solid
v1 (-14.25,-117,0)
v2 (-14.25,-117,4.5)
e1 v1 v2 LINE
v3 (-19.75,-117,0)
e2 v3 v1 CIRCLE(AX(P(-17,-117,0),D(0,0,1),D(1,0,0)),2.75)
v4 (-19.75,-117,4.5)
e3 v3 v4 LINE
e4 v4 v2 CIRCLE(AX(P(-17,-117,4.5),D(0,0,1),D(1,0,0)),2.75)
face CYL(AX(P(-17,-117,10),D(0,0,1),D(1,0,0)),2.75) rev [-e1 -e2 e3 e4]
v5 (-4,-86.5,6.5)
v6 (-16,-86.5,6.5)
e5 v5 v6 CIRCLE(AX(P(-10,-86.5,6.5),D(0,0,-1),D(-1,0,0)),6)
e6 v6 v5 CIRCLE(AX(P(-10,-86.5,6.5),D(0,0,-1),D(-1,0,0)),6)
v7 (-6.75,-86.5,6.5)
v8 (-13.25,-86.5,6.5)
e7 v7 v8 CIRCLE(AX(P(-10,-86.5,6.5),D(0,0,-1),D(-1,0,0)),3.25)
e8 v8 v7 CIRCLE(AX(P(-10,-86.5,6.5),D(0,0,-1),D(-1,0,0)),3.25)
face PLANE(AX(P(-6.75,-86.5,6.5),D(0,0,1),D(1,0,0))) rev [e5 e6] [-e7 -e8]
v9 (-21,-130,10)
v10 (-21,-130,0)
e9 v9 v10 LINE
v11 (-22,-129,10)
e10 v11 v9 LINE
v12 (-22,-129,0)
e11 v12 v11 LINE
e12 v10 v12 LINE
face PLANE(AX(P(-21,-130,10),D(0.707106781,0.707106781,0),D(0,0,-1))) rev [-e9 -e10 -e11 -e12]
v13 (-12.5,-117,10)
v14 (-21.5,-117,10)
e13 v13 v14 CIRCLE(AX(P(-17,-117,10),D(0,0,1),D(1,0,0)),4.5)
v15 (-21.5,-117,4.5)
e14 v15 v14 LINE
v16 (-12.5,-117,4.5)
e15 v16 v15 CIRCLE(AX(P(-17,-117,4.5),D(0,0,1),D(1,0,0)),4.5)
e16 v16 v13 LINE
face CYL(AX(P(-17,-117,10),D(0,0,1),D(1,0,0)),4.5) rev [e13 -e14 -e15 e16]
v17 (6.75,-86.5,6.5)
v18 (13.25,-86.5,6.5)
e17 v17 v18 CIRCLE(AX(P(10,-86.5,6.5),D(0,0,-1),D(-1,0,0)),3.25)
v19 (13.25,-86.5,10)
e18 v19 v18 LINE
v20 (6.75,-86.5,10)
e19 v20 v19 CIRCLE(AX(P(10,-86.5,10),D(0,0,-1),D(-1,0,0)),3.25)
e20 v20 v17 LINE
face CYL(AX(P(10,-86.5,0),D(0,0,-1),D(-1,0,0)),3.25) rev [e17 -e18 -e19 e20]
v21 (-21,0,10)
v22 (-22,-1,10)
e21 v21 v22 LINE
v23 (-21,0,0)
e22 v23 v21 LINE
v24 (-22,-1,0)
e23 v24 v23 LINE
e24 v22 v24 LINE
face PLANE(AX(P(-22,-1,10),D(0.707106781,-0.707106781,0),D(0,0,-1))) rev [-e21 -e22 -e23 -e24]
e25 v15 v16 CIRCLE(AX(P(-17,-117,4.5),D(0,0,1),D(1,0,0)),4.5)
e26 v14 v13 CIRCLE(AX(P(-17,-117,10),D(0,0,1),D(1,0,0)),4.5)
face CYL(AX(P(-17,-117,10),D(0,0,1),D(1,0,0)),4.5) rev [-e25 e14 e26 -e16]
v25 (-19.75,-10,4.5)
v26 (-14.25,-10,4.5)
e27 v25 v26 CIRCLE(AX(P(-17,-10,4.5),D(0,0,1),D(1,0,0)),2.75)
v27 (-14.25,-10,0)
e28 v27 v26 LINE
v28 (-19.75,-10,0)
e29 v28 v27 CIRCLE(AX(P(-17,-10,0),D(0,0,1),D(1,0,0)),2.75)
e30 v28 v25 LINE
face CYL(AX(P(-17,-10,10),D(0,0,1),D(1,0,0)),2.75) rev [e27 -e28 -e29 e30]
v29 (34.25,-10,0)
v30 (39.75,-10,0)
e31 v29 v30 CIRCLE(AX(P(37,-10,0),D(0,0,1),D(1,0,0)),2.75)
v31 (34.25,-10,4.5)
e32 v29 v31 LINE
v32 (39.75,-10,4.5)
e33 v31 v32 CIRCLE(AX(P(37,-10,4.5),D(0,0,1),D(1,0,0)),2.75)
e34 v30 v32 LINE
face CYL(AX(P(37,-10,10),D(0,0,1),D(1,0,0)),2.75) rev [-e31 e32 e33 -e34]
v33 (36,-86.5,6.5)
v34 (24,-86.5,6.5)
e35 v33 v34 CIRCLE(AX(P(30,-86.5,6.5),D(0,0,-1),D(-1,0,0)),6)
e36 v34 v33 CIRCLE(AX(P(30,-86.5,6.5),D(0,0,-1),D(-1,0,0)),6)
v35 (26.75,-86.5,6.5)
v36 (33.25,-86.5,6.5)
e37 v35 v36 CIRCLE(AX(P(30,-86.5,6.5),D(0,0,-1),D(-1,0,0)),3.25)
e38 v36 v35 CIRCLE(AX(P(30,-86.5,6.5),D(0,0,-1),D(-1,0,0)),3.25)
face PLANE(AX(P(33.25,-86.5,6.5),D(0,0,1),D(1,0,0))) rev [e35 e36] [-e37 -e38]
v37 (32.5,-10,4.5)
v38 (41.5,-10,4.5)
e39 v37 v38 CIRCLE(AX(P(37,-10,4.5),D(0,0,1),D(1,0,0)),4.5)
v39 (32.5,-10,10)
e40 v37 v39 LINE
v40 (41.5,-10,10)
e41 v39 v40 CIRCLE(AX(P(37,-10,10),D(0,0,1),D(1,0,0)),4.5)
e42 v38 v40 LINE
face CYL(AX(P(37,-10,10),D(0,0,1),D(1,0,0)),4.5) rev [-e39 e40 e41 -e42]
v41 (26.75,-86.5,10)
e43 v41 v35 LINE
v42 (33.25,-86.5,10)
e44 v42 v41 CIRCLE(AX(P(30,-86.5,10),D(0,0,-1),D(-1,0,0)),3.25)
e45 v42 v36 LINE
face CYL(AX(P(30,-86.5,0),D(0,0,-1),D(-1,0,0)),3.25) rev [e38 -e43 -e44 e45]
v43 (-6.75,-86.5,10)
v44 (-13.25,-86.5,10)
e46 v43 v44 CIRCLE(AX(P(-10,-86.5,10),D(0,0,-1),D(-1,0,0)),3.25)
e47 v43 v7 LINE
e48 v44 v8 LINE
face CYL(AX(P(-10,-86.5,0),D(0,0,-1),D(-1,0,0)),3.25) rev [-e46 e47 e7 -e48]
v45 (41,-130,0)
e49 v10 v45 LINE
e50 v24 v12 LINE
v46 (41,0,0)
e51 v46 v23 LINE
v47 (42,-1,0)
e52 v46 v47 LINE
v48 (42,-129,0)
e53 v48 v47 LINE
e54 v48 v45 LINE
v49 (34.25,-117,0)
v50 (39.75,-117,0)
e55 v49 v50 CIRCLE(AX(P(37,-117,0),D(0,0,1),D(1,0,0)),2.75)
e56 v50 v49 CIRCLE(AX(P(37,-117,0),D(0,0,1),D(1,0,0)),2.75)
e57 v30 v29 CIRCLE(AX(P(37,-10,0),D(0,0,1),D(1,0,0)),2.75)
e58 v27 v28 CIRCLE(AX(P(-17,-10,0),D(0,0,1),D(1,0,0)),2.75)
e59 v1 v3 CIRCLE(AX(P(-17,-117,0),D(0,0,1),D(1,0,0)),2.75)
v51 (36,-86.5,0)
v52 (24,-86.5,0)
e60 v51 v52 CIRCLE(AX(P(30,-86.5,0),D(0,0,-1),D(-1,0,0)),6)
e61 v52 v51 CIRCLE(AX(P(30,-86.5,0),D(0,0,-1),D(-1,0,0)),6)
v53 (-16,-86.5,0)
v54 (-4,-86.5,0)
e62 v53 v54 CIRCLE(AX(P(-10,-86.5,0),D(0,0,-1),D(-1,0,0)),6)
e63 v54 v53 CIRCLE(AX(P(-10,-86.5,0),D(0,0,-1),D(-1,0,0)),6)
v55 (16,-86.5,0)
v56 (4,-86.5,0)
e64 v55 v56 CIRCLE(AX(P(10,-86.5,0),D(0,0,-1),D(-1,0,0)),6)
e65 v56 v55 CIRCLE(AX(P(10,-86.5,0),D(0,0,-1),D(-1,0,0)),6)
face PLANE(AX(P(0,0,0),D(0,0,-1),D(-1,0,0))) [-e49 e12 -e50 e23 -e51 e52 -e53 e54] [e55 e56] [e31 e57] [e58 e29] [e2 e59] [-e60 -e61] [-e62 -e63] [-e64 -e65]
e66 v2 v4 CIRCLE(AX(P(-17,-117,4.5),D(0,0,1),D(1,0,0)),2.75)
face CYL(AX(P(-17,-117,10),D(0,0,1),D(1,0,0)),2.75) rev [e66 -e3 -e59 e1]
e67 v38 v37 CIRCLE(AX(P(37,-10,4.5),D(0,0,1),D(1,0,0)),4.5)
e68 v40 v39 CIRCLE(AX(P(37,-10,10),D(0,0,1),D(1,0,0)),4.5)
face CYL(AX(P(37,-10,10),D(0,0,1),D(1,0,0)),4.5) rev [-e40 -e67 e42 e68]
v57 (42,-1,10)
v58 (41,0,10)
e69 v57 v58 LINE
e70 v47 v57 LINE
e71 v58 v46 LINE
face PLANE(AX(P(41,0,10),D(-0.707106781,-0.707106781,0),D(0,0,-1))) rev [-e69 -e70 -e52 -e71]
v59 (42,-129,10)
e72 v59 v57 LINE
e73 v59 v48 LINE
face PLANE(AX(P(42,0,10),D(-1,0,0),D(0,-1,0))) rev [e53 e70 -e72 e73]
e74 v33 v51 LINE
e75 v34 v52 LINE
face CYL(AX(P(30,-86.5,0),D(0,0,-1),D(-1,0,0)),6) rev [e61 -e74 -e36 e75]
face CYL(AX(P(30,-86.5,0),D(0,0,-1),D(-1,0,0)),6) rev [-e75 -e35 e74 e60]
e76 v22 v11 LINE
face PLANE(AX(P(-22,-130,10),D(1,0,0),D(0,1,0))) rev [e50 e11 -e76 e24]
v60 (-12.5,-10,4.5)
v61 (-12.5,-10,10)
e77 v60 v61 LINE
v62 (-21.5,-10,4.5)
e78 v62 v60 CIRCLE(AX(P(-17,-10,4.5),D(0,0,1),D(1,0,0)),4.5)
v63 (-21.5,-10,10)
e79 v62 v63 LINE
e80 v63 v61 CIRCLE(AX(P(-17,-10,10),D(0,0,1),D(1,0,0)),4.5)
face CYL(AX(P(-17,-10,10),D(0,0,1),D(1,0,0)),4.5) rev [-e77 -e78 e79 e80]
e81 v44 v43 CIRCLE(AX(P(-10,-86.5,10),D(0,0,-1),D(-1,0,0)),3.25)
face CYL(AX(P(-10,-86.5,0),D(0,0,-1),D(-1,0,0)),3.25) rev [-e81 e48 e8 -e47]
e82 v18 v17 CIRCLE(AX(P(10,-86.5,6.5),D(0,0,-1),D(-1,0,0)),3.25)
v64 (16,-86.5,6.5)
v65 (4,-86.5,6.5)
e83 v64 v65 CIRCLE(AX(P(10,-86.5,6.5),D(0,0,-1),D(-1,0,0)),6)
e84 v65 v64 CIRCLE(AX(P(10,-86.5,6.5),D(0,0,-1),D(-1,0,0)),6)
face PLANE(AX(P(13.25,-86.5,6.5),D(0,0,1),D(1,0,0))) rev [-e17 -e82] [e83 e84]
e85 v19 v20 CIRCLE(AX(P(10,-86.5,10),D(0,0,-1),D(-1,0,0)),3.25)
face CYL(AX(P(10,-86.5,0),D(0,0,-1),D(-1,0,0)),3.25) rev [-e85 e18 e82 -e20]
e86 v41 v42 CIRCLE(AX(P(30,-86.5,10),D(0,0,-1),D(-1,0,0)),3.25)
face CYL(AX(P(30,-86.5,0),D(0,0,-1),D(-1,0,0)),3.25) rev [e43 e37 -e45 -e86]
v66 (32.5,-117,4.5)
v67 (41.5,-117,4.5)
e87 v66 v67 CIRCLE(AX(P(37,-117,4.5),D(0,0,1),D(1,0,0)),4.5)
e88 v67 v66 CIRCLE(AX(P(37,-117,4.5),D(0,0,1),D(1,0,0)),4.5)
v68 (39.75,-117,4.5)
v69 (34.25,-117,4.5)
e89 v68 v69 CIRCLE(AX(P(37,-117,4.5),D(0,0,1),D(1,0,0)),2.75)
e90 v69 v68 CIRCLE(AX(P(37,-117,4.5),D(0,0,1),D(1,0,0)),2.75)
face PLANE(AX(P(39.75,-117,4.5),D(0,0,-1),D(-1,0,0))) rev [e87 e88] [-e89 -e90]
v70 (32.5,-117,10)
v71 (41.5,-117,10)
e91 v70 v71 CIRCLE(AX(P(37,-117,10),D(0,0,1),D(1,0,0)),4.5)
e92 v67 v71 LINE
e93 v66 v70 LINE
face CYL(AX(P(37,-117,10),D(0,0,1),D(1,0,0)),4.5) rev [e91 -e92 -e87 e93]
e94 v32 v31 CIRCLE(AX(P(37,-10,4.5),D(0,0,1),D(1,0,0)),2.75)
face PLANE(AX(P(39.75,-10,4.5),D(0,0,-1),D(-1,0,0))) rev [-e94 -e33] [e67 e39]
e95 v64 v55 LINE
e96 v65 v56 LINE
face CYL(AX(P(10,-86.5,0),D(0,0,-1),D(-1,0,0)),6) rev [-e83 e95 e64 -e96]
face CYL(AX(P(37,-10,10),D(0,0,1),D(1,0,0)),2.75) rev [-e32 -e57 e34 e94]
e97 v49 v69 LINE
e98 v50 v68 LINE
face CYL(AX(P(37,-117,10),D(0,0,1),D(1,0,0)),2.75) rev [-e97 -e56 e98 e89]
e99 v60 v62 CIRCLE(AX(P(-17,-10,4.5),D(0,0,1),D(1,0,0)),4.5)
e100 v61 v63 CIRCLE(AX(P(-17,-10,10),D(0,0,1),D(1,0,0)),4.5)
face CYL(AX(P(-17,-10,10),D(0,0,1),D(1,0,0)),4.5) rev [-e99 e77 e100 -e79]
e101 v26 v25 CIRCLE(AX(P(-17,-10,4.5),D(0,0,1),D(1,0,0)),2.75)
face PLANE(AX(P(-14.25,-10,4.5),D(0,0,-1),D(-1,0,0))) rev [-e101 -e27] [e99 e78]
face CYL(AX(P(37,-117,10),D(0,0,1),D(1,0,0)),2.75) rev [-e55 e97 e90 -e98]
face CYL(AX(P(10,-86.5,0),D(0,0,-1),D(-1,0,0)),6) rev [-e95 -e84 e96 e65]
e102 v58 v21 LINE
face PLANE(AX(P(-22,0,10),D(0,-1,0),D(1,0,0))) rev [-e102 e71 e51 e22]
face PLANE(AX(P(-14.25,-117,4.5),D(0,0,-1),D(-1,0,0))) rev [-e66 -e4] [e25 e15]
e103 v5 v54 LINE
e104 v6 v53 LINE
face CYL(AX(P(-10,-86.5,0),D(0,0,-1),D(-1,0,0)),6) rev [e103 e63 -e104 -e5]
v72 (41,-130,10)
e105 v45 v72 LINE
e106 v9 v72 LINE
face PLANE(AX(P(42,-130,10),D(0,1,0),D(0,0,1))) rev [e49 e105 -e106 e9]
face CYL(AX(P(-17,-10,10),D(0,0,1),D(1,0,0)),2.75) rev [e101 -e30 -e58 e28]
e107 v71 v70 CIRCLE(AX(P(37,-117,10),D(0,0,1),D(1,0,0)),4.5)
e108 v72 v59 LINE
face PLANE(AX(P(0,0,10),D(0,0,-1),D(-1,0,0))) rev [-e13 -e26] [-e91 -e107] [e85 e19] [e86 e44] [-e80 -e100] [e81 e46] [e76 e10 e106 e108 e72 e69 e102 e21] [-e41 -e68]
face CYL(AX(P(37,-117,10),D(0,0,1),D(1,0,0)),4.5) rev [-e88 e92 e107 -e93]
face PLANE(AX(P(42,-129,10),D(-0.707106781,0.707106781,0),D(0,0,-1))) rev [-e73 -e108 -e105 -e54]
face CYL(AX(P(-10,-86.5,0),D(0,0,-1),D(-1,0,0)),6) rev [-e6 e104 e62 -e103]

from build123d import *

# Parameters (mm, degrees)
SKETCH_1_W                  = 64
SKETCH_1_H                  = 130
EXTRUDE_1_DEPTH             = 10
HOLE_WIZARD_0_D             = 5.5
HOLE_WIZARD_0_CBORE_D       = 9
HOLE_WIZARD_0_CBORE_DEPTH   = 5.5
HOLE_WIZARD_C_1_D           = 6.5
HOLE_WIZARD_C_1_CBORE_D     = 12
HOLE_WIZARD_C_1_CBORE_DEPTH = 6.5
CHAMFER_1_SIZE              = 1


with BuildPart() as part:
    # 草图1 → 凸台-拉伸1 (new body)
    with BuildSketch(Plane.XY):
        with Locations((10, -65)):
            Rectangle(SKETCH_1_W, SKETCH_1_H)
    extrude(amount=EXTRUDE_1_DEPTH)

    # 打孔尺寸根据内六角圆柱头螺钉的类型0 (through all)
    with Locations(Plane.XY.offset(10)):
        with Locations((-17, -10), (37, -10), (-17, -117), (37, -117)):
            CounterBoreHole(HOLE_WIZARD_0_D / 2, HOLE_WIZARD_0_CBORE_D / 2, HOLE_WIZARD_0_CBORE_DEPTH)

    # 打孔尺寸根据六角头螺栓 C 级的类型1 (through all)
    with Locations(Plane(origin=(0, 0, 0), x_dir=(-1, 0, 0), z_dir=(0, 0, -1))):
        with Locations((10, -86.5), (-10, -86.5), (-30, -86.5)):
            CounterBoreHole(HOLE_WIZARD_C_1_D / 2, HOLE_WIZARD_C_1_CBORE_D / 2, HOLE_WIZARD_C_1_CBORE_DEPTH)

    # 倒角1
    chamfer_1_edges = [part.edges().sort_by_distance(p)[0] for p in [
        (-22, 0, 5),
        (42, 0, 5),
        (42, -130, 5),
        (-22, -130, 5),
    ]]
    chamfer(chamfer_1_edges, length=CHAMFER_1_SIZE)


solid = part.part
